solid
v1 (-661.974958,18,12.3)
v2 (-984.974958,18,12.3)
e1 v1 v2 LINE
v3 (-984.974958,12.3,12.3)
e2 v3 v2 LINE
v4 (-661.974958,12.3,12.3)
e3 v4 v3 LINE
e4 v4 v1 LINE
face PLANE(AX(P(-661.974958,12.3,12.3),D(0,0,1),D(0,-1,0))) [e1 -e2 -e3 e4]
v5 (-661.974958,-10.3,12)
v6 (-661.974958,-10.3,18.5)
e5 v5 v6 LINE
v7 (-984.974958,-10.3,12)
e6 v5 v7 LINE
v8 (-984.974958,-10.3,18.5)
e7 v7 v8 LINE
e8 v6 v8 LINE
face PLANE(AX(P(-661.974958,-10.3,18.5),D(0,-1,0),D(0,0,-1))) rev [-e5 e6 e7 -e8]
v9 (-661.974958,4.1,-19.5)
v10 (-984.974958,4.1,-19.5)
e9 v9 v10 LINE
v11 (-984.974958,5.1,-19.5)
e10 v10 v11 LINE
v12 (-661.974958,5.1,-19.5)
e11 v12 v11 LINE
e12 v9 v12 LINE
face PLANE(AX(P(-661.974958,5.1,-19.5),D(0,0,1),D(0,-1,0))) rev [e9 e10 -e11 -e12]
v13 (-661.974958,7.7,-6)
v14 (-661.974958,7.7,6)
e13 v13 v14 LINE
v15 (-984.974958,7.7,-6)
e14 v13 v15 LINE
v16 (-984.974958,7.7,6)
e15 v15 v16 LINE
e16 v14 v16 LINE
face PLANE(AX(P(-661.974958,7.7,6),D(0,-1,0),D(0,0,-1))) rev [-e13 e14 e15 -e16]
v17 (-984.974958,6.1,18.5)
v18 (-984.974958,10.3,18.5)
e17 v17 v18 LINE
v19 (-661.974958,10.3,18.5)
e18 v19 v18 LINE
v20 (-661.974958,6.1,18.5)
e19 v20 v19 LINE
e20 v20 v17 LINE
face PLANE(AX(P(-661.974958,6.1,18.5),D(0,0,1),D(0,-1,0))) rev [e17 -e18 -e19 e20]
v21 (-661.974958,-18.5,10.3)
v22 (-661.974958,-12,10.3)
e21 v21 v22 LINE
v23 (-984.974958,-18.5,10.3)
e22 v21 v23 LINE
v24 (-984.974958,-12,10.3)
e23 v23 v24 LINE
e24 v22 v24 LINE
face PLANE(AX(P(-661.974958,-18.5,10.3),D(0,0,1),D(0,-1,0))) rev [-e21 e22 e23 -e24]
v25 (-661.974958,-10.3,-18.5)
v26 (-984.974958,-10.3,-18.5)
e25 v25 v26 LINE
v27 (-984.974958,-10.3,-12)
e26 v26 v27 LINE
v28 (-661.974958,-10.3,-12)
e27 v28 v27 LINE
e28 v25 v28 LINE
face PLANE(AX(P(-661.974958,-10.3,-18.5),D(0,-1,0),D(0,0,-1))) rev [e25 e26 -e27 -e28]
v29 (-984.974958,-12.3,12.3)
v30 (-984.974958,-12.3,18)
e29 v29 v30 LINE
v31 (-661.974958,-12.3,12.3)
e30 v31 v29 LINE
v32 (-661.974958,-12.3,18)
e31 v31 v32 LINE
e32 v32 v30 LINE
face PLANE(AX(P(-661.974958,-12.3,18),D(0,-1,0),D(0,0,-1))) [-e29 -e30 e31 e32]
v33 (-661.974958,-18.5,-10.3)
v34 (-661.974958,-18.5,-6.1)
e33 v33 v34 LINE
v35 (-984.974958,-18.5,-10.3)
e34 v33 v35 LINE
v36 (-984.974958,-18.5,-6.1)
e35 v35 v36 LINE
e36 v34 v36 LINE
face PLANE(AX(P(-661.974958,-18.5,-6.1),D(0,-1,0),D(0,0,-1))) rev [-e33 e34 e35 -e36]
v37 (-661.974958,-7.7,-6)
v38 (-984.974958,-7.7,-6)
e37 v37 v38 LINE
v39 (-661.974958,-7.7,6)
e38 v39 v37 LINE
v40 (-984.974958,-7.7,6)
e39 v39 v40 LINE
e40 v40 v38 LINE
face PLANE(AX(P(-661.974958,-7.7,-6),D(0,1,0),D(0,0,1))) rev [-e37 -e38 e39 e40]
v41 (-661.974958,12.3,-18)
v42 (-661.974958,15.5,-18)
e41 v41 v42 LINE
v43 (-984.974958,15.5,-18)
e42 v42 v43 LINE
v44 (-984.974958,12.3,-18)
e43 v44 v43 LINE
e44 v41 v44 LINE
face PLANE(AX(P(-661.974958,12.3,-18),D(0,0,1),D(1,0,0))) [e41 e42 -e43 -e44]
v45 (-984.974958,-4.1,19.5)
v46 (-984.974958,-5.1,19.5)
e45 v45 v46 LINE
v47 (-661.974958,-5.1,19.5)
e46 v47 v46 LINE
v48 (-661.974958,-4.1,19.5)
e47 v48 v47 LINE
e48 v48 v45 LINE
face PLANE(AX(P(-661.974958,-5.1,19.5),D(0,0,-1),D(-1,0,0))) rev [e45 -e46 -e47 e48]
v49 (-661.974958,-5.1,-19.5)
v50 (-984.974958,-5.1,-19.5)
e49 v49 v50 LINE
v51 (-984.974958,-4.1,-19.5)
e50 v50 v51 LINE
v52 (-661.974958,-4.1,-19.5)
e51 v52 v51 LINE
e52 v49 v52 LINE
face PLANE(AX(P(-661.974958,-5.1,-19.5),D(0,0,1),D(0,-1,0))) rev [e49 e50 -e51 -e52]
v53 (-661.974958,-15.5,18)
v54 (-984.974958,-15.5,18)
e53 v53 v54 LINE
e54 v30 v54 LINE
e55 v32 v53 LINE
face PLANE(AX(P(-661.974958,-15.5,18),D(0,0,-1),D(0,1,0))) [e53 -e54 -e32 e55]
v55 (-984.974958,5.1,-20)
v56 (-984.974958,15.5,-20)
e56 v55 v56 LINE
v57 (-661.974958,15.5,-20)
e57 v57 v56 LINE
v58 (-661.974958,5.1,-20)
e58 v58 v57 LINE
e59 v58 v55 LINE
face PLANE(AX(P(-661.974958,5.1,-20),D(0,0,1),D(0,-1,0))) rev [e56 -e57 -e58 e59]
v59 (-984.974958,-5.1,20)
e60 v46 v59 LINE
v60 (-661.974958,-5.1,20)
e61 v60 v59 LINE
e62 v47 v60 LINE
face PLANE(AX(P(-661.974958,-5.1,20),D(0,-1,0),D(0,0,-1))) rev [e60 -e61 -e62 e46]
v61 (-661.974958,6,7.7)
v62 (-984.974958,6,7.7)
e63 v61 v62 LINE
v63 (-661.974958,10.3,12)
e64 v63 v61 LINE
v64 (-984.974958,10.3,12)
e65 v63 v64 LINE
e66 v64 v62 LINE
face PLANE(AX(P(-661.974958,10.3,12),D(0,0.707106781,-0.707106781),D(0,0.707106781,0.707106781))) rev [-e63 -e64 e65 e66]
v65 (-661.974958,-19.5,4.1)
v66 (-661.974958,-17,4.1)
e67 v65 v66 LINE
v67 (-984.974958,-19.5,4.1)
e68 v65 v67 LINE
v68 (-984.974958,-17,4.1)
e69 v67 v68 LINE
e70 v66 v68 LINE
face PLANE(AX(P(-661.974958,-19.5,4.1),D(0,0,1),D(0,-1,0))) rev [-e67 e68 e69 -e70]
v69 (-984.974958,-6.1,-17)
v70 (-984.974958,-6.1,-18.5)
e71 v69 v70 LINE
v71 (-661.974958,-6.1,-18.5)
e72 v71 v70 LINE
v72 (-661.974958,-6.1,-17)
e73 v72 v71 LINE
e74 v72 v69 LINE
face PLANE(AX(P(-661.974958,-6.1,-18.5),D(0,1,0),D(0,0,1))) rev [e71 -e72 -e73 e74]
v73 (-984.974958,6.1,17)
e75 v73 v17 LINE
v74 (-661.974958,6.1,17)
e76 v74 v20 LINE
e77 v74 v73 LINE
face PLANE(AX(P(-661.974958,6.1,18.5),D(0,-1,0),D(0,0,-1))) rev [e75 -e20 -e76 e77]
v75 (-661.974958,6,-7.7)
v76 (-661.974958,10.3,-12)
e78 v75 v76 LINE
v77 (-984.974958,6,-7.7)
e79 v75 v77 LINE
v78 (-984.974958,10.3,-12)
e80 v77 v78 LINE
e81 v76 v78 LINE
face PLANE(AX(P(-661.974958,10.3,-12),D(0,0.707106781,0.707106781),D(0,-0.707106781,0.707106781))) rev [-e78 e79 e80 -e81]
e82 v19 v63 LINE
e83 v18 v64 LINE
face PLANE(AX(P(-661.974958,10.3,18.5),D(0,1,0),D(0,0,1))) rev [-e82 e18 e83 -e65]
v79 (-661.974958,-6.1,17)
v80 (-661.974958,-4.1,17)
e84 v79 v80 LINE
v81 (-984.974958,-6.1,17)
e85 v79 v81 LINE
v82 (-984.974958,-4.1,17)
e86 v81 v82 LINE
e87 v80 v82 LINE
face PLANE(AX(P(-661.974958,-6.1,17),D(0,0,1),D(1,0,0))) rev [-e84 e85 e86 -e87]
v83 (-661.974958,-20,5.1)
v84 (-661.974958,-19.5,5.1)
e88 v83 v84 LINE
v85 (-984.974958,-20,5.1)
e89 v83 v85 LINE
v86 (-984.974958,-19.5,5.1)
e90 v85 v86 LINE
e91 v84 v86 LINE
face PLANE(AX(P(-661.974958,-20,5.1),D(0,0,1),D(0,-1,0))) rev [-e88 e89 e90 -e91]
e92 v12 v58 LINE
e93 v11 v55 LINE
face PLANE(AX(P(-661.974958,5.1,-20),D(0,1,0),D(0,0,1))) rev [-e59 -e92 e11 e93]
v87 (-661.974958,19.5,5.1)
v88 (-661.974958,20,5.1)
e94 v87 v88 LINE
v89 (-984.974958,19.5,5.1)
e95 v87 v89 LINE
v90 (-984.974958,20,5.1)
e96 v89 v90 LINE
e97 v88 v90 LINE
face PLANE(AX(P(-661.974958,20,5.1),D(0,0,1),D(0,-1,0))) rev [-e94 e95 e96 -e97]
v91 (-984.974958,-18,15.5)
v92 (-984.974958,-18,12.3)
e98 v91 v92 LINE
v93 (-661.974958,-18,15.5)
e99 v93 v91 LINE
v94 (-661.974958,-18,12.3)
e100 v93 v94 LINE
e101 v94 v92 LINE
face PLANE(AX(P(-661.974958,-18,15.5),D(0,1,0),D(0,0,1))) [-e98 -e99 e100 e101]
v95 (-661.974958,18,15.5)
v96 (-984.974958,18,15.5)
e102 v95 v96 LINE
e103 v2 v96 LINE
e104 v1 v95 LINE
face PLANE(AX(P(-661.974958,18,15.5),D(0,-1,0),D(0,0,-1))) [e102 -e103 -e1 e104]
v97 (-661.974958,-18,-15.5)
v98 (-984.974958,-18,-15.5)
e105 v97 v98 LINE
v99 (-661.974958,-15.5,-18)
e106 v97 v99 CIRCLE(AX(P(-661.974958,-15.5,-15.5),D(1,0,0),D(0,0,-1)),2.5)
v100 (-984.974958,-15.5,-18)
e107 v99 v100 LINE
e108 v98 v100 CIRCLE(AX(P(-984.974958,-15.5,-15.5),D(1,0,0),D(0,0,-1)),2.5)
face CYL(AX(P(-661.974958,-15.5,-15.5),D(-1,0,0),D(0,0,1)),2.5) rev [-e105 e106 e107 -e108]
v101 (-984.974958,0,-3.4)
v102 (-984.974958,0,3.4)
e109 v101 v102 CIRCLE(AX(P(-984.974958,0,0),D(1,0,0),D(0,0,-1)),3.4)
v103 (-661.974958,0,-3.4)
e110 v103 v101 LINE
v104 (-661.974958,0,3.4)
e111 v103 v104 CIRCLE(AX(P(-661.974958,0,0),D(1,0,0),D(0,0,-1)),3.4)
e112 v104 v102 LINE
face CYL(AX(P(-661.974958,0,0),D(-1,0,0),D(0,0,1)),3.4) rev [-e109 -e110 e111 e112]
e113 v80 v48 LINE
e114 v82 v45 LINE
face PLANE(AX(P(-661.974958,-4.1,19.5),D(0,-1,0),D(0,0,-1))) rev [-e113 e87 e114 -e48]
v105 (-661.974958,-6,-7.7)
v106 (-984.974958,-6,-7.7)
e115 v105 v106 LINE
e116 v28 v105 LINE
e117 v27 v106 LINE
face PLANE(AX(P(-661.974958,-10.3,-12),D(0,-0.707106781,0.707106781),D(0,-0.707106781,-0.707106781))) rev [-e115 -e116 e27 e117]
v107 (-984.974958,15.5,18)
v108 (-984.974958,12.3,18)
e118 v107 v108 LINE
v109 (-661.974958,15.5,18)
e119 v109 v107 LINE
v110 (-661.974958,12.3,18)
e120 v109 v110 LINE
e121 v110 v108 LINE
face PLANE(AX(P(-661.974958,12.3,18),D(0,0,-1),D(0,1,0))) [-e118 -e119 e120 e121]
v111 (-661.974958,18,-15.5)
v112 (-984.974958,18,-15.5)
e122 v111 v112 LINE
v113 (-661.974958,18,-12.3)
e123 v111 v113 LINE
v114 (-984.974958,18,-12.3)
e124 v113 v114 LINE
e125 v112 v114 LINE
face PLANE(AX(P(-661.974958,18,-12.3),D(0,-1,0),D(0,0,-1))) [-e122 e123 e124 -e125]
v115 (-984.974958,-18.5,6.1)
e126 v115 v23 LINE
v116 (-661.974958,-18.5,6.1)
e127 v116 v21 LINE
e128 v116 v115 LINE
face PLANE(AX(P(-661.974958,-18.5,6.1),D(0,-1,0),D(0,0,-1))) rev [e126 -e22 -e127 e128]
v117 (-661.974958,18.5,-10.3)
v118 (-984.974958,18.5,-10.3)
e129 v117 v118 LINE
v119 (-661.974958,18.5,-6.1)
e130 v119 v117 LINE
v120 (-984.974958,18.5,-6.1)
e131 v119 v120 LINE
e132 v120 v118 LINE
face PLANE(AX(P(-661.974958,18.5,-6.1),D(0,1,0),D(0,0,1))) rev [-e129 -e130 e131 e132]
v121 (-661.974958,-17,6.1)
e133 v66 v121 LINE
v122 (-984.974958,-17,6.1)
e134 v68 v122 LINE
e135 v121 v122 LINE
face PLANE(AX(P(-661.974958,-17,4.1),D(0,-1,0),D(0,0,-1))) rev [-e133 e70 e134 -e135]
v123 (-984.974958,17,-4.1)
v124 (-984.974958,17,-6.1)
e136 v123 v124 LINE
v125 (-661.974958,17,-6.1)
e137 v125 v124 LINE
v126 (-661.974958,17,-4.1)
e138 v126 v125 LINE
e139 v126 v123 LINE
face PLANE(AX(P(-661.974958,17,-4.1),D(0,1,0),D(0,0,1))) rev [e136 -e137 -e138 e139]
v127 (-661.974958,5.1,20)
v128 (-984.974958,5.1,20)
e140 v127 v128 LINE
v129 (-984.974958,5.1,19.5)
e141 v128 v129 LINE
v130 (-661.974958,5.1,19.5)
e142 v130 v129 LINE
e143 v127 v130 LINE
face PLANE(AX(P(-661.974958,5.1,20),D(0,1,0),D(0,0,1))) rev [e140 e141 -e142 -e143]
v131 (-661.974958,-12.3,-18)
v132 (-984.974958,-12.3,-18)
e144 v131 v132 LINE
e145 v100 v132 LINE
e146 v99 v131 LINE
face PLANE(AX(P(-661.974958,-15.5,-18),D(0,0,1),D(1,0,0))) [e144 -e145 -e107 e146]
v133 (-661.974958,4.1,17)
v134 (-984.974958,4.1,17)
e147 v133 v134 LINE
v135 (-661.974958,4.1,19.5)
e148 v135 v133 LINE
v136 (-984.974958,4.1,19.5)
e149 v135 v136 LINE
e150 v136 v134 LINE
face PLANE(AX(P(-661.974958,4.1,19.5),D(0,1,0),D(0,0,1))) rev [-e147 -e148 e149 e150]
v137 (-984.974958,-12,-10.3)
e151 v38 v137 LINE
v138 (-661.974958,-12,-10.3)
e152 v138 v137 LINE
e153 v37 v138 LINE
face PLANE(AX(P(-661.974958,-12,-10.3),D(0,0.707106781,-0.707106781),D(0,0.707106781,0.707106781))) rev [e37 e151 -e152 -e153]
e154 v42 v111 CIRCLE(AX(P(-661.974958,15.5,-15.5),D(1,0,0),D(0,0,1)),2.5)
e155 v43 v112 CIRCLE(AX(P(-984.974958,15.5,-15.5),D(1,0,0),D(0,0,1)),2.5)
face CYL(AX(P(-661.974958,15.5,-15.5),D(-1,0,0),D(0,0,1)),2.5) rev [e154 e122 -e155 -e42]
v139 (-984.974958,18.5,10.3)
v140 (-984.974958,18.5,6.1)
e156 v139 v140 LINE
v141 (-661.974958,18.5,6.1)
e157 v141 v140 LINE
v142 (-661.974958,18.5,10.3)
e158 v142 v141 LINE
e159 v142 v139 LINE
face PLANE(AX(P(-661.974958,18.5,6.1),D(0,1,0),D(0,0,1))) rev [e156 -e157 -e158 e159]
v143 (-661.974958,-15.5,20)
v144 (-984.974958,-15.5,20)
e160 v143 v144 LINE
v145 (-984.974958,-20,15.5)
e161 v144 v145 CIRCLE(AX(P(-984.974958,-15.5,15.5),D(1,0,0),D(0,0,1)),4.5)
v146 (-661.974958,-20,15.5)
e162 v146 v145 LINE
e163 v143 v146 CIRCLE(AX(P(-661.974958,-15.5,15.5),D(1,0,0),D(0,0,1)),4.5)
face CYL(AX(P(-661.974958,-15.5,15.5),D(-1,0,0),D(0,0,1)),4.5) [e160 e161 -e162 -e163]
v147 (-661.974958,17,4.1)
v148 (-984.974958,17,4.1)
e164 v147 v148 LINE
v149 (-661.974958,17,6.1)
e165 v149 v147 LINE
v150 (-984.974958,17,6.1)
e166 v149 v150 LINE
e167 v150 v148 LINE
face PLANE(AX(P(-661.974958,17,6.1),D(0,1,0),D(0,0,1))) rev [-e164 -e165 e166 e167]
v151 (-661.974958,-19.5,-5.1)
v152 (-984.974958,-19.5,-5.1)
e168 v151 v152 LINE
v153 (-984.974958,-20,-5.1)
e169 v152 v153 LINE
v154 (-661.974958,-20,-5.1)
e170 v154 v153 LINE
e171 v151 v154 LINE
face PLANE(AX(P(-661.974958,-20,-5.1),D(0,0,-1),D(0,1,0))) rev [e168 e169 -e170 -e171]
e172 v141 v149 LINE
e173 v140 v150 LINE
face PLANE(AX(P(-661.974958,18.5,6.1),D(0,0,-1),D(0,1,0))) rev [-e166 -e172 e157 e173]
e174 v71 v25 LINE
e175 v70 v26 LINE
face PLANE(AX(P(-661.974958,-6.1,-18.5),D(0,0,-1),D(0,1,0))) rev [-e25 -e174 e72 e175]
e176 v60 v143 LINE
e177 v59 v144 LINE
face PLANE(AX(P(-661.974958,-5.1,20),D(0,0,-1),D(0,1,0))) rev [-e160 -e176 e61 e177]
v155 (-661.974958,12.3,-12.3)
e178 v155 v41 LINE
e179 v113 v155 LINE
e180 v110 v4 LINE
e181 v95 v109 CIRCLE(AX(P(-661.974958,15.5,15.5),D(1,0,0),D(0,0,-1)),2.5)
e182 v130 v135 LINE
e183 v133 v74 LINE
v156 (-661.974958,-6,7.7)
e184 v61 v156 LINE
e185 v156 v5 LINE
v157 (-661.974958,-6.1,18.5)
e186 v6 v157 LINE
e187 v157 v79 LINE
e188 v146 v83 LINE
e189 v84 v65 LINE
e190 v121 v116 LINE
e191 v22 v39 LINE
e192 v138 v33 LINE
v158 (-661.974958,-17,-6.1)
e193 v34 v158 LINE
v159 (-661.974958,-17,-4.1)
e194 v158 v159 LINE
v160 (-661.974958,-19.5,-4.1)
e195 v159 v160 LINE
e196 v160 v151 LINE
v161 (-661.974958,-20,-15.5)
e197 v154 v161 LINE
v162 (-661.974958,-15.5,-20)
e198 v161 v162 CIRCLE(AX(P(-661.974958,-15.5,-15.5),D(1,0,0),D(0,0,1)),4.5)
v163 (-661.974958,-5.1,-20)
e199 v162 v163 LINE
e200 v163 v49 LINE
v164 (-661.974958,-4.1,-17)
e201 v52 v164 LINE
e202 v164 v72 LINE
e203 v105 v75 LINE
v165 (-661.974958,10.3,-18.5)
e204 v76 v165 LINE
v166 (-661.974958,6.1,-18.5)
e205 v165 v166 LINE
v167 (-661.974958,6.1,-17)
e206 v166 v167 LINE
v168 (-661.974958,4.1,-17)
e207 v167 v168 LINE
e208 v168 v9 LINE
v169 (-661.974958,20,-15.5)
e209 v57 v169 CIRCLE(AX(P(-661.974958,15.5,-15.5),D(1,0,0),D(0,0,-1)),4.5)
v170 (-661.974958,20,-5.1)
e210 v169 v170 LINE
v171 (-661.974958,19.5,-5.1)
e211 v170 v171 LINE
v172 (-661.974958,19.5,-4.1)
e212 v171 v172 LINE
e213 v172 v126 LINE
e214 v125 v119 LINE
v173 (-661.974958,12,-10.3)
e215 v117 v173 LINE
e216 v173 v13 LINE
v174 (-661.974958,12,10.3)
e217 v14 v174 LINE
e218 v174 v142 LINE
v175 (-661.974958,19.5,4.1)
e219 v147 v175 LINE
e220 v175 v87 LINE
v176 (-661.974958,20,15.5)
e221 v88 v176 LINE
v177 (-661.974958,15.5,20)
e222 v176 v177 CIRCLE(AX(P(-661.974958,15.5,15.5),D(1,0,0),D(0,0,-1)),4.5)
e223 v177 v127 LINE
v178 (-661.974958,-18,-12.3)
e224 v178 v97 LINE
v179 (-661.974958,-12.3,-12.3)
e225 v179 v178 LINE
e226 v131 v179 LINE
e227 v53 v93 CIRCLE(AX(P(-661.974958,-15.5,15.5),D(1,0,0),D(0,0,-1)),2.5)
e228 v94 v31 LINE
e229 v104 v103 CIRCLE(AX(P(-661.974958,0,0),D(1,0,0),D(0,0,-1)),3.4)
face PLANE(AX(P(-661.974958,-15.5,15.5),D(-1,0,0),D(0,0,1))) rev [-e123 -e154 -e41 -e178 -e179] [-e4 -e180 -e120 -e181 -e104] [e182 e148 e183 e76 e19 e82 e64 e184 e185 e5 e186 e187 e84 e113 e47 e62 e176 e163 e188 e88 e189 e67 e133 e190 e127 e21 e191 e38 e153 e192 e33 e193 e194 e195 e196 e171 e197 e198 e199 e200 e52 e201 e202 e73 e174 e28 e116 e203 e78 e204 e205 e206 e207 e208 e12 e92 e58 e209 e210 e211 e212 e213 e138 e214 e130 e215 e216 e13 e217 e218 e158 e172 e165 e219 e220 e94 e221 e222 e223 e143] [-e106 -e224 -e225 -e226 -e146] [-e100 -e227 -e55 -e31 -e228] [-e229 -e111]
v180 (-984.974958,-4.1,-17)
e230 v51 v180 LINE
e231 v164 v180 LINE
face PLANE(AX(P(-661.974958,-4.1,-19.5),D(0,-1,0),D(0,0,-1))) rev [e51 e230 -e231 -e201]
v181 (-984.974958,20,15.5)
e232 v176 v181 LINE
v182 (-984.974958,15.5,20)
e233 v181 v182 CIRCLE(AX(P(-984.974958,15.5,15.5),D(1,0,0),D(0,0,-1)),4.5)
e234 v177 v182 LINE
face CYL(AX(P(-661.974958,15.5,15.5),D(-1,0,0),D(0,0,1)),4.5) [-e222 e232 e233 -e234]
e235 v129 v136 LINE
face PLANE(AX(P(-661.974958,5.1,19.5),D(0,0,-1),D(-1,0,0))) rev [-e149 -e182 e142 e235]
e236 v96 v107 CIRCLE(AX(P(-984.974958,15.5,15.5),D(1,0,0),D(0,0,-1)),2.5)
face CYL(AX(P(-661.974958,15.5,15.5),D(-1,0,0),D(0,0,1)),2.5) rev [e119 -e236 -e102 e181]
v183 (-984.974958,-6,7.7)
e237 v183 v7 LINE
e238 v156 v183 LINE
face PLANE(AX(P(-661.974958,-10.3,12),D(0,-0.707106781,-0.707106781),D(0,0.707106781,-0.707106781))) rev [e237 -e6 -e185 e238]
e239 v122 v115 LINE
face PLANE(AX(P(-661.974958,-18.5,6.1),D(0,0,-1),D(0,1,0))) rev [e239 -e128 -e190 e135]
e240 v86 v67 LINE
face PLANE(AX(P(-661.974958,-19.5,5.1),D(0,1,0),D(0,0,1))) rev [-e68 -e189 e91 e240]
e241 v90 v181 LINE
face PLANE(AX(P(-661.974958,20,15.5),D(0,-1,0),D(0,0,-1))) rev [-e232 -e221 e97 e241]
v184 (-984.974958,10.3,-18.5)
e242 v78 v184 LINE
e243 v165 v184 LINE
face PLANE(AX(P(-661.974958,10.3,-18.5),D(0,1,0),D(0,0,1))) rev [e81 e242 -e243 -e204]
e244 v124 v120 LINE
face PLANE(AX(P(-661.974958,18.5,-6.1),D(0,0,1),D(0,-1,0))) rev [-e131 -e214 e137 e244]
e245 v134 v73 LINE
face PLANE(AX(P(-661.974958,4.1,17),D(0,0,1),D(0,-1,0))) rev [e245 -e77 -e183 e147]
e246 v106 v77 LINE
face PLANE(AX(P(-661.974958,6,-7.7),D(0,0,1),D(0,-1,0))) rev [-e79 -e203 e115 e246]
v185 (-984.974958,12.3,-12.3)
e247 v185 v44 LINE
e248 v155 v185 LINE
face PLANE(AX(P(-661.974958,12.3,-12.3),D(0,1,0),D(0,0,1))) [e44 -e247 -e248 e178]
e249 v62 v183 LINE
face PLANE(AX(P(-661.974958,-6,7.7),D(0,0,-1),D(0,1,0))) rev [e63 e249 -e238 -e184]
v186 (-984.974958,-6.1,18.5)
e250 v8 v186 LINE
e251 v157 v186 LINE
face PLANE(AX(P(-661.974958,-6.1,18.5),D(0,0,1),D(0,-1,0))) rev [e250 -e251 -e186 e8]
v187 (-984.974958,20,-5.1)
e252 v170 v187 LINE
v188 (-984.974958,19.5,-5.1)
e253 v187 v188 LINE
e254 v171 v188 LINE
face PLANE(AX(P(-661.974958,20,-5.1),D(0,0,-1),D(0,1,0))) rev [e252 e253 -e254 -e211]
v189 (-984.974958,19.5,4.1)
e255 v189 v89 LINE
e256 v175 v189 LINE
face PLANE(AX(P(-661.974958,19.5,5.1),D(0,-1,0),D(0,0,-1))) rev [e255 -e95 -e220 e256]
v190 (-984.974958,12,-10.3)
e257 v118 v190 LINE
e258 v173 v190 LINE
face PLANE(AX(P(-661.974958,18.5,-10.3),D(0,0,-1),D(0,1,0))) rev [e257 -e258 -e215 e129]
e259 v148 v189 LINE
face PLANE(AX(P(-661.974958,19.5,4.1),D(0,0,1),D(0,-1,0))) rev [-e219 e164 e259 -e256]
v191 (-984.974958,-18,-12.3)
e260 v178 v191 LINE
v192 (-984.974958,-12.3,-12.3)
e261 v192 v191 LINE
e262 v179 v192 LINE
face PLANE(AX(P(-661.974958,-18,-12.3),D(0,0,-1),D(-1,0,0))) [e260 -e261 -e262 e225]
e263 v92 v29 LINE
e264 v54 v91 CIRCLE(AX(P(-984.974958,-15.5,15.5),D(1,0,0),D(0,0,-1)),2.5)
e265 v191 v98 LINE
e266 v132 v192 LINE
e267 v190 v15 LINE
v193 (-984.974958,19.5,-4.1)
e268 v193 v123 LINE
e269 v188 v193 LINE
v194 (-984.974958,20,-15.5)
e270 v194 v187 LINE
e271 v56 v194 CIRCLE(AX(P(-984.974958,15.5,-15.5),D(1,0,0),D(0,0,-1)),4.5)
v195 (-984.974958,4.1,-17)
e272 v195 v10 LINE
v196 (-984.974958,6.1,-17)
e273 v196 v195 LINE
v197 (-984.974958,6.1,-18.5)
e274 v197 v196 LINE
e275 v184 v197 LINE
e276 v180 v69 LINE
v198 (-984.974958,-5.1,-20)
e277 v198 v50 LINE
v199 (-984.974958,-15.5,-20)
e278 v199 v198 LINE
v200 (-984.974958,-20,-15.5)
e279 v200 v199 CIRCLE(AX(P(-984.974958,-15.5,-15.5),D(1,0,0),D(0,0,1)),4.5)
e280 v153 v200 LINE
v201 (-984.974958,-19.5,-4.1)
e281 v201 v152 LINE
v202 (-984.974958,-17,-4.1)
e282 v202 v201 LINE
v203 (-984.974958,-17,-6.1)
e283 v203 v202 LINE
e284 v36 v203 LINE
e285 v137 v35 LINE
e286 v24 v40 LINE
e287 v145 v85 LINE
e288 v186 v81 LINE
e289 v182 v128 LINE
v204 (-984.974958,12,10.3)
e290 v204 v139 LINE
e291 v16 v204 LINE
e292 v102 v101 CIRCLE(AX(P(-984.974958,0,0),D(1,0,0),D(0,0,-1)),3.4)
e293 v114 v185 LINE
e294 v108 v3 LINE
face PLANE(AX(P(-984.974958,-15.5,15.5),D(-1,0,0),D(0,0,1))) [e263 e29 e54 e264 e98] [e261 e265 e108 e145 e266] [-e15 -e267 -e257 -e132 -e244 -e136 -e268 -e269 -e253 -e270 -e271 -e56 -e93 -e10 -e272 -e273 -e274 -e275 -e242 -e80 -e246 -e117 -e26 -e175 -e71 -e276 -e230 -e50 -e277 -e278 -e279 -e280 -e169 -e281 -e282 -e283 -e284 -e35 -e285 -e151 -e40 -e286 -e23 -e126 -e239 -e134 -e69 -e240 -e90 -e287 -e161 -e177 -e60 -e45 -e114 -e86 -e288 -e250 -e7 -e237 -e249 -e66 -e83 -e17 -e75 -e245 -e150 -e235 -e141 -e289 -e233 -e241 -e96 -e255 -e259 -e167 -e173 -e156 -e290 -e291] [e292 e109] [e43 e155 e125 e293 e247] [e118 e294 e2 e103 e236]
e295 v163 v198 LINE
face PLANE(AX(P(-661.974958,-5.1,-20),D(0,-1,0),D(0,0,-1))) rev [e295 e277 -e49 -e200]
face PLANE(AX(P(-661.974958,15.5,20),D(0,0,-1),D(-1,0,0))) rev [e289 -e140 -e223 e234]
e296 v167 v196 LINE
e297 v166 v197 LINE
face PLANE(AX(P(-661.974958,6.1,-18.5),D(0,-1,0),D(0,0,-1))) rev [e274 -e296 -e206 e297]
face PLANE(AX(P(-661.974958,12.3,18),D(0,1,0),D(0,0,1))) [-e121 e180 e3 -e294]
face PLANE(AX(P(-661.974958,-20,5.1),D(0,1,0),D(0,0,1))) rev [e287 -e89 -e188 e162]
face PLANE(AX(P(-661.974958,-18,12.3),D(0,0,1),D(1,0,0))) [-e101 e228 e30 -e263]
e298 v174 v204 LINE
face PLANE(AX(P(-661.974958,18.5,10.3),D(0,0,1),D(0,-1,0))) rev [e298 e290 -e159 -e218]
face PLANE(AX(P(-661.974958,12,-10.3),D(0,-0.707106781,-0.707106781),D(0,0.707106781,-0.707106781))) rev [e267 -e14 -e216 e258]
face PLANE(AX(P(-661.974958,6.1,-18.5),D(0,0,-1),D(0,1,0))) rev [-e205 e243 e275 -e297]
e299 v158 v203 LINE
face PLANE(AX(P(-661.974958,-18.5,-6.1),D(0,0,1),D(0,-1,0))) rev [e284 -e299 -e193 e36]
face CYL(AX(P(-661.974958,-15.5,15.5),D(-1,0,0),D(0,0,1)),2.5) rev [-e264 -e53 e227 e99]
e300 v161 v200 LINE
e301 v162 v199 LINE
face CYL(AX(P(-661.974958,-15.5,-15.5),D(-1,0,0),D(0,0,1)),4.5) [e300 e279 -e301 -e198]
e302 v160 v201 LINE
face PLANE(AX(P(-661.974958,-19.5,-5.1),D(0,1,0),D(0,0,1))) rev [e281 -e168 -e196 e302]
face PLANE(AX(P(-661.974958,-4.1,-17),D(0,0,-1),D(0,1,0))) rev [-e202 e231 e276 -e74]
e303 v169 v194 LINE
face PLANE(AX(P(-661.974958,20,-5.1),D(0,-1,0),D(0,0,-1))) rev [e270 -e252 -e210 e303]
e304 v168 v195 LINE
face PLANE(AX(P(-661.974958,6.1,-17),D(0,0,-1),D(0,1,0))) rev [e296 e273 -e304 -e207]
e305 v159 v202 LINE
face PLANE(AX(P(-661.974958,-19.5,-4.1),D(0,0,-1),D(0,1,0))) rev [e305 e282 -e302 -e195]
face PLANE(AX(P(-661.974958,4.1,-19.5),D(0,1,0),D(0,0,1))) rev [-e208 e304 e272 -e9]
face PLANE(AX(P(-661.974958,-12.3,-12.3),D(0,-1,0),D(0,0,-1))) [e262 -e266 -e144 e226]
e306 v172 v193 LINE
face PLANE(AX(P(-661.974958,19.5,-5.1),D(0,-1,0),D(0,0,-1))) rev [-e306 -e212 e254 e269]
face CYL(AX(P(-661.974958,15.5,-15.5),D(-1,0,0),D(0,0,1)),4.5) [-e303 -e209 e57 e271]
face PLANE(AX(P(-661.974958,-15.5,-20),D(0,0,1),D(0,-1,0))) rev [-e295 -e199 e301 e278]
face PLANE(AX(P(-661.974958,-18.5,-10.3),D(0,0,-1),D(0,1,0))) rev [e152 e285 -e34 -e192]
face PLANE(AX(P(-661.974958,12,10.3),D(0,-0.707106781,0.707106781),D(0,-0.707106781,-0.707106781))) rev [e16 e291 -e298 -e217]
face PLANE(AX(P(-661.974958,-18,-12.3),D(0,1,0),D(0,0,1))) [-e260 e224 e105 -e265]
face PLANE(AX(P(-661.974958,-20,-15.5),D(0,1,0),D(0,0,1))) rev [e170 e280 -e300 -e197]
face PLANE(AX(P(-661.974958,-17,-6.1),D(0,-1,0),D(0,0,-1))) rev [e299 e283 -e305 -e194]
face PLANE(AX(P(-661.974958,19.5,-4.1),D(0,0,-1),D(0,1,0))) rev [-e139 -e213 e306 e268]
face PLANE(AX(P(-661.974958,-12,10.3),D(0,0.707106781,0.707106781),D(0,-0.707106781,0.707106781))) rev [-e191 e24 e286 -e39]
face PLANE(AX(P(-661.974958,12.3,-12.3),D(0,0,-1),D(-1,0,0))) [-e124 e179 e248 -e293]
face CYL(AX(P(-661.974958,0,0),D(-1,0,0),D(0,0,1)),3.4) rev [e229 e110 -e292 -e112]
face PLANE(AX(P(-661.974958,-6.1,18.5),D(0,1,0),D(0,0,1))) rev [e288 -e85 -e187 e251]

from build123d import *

# Parameters (mm, degrees)
SKETCH1_R                                 = 3.4
ALUMINIUM_PROFILE_40_X_40B_X_R4_5_1_DEPTH = 323


with BuildPart() as part:
    # Sketch1 → Aluminium profile 40 X 40B X R4.5(1) (new body)
    with BuildSketch(Plane.YZ.offset(-984.974958264)):
        with BuildLine():
            Line((-5.1, 20), (-5.1, 19.5))
            Line((-5.1, 19.5), (-4.1, 19.5))
            Line((-4.1, 19.5), (-4.1, 17))
            Line((-4.1, 17), (-6.1, 17))
            Line((-6.1, 17), (-6.1, 18.5))
            Line((-6.1, 18.5), (-10.3, 18.5))
            Line((-10.3, 18.5), (-10.3, 12))
            Line((-10.3, 12), (-6, 7.7))
            Line((-6, 7.7), (6, 7.7))
            Line((6, 7.7), (10.3, 12))
            Line((10.3, 12), (10.3, 18.5))
            Line((10.3, 18.5), (6.1, 18.5))
            Line((6.1, 18.5), (6.1, 17))
            Line((6.1, 17), (4.1, 17))
            Line((4.1, 17), (4.1, 19.5))
            Line((4.1, 19.5), (5.1, 19.5))
            Line((5.1, 19.5), (5.1, 20))
            Line((5.1, 20), (15.5, 20))
            ThreePointArc((15.5, 20), (18.681980515, 18.681980515), (20, 15.5))
            Line((20, 15.5), (20, 5.1))
            Line((20, 5.1), (19.5, 5.1))
            Line((19.5, 5.1), (19.5, 4.1))
            Line((19.5, 4.1), (17, 4.1))
            Line((17, 4.1), (17, 6.1))
            Line((17, 6.1), (18.5, 6.1))
            Line((18.5, 6.1), (18.5, 10.3))
            Line((18.5, 10.3), (12, 10.3))
            Line((12, 10.3), (7.7, 6))
            Line((7.7, 6), (7.7, -6))
            Line((7.7, -6), (12, -10.3))
            Line((12, -10.3), (18.5, -10.3))
            Line((18.5, -10.3), (18.5, -6.1))
            Line((18.5, -6.1), (17, -6.1))
            Line((17, -6.1), (17, -4.1))
            Line((17, -4.1), (19.5, -4.1))
            Line((19.5, -4.1), (19.5, -5.1))
            Line((19.5, -5.1), (20, -5.1))
            Line((20, -5.1), (20, -15.5))
            ThreePointArc((20, -15.5), (18.681980515, -18.681980515), (15.5, -20))
            Line((15.5, -20), (5.1, -20))
            Line((5.1, -20), (5.1, -19.5))
            Line((5.1, -19.5), (4.1, -19.5))
            Line((4.1, -19.5), (4.1, -17))
            Line((4.1, -17), (6.1, -17))
            Line((6.1, -17), (6.1, -18.5))
            Line((6.1, -18.5), (10.3, -18.5))
            Line((10.3, -18.5), (10.3, -12))
            Line((10.3, -12), (6, -7.7))
            Line((6, -7.7), (-6, -7.7))
            Line((-6, -7.7), (-10.3, -12))
            Line((-10.3, -12), (-10.3, -18.5))
            Line((-10.3, -18.5), (-6.1, -18.5))
            Line((-6.1, -18.5), (-6.1, -17))
            Line((-6.1, -17), (-4.1, -17))
            Line((-4.1, -17), (-4.1, -19.5))
            Line((-4.1, -19.5), (-5.1, -19.5))
            Line((-5.1, -19.5), (-5.1, -20))
            Line((-5.1, -20), (-15.5, -20))
            ThreePointArc((-15.5, -20), (-18.681980515, -18.681980515), (-20, -15.5))
            Line((-20, -15.5), (-20, -5.1))
            Line((-20, -5.1), (-19.5, -5.1))
            Line((-19.5, -5.1), (-19.5, -4.1))
            Line((-19.5, -4.1), (-17, -4.1))
            Line((-17, -4.1), (-17, -6.1))
            Line((-17, -6.1), (-18.5, -6.1))
            Line((-18.5, -6.1), (-18.5, -10.3))
            Line((-18.5, -10.3), (-12, -10.3))
            Line((-12, -10.3), (-7.7, -6))
            Line((-7.7, -6), (-7.7, 6))
            Line((-7.7, 6), (-12, 10.3))
            Line((-12, 10.3), (-18.5, 10.3))
            Line((-18.5, 10.3), (-18.5, 6.1))
            Line((-18.5, 6.1), (-17, 6.1))
            Line((-17, 6.1), (-17, 4.1))
            Line((-17, 4.1), (-19.5, 4.1))
            Line((-19.5, 4.1), (-19.5, 5.1))
            Line((-19.5, 5.1), (-20, 5.1))
            Line((-20, 5.1), (-20, 15.5))
            ThreePointArc((-20, 15.5), (-18.681980515, 18.681980515), (-15.5, 20))
            Line((-15.5, 20), (-5.1, 20))
        make_face()
        Circle(SKETCH1_R, mode=Mode.SUBTRACT)
        with BuildLine():
            Line((12.3, 18), (15.5, 18))
            ThreePointArc((15.5, 18), (17.267766953, 17.267766953), (18, 15.5))
            Line((18, 15.5), (18, 12.3))
            Line((18, 12.3), (12.3, 12.3))
            Line((12.3, 12.3), (12.3, 18))
        make_face(mode=Mode.SUBTRACT)
        with BuildLine():
            Line((-15.5, 18), (-12.3, 18))
            Line((-12.3, 18), (-12.3, 12.3))
            Line((-12.3, 12.3), (-18, 12.3))
            Line((-18, 12.3), (-18, 15.5))
            ThreePointArc((-18, 15.5), (-17.267766953, 17.267766953), (-15.5, 18))
        make_face(mode=Mode.SUBTRACT)
        with BuildLine():
            Line((-18, -12.3), (-12.3, -12.3))
            Line((-12.3, -12.3), (-12.3, -18))
            Line((-12.3, -18), (-15.5, -18))
            ThreePointArc((-15.5, -18), (-17.267766953, -17.267766953), (-18, -15.5))
            Line((-18, -15.5), (-18, -12.3))
        make_face(mode=Mode.SUBTRACT)
        with BuildLine():
            Line((12.3, -12.3), (18, -12.3))
            Line((18, -12.3), (18, -15.5))
            ThreePointArc((18, -15.5), (17.267766953, -17.267766953), (15.5, -18))
            Line((15.5, -18), (12.3, -18))
            Line((12.3, -18), (12.3, -12.3))
        make_face(mode=Mode.SUBTRACT)
    extrude(amount=ALUMINIUM_PROFILE_40_X_40B_X_R4_5_1_DEPTH)


solid = part.part
